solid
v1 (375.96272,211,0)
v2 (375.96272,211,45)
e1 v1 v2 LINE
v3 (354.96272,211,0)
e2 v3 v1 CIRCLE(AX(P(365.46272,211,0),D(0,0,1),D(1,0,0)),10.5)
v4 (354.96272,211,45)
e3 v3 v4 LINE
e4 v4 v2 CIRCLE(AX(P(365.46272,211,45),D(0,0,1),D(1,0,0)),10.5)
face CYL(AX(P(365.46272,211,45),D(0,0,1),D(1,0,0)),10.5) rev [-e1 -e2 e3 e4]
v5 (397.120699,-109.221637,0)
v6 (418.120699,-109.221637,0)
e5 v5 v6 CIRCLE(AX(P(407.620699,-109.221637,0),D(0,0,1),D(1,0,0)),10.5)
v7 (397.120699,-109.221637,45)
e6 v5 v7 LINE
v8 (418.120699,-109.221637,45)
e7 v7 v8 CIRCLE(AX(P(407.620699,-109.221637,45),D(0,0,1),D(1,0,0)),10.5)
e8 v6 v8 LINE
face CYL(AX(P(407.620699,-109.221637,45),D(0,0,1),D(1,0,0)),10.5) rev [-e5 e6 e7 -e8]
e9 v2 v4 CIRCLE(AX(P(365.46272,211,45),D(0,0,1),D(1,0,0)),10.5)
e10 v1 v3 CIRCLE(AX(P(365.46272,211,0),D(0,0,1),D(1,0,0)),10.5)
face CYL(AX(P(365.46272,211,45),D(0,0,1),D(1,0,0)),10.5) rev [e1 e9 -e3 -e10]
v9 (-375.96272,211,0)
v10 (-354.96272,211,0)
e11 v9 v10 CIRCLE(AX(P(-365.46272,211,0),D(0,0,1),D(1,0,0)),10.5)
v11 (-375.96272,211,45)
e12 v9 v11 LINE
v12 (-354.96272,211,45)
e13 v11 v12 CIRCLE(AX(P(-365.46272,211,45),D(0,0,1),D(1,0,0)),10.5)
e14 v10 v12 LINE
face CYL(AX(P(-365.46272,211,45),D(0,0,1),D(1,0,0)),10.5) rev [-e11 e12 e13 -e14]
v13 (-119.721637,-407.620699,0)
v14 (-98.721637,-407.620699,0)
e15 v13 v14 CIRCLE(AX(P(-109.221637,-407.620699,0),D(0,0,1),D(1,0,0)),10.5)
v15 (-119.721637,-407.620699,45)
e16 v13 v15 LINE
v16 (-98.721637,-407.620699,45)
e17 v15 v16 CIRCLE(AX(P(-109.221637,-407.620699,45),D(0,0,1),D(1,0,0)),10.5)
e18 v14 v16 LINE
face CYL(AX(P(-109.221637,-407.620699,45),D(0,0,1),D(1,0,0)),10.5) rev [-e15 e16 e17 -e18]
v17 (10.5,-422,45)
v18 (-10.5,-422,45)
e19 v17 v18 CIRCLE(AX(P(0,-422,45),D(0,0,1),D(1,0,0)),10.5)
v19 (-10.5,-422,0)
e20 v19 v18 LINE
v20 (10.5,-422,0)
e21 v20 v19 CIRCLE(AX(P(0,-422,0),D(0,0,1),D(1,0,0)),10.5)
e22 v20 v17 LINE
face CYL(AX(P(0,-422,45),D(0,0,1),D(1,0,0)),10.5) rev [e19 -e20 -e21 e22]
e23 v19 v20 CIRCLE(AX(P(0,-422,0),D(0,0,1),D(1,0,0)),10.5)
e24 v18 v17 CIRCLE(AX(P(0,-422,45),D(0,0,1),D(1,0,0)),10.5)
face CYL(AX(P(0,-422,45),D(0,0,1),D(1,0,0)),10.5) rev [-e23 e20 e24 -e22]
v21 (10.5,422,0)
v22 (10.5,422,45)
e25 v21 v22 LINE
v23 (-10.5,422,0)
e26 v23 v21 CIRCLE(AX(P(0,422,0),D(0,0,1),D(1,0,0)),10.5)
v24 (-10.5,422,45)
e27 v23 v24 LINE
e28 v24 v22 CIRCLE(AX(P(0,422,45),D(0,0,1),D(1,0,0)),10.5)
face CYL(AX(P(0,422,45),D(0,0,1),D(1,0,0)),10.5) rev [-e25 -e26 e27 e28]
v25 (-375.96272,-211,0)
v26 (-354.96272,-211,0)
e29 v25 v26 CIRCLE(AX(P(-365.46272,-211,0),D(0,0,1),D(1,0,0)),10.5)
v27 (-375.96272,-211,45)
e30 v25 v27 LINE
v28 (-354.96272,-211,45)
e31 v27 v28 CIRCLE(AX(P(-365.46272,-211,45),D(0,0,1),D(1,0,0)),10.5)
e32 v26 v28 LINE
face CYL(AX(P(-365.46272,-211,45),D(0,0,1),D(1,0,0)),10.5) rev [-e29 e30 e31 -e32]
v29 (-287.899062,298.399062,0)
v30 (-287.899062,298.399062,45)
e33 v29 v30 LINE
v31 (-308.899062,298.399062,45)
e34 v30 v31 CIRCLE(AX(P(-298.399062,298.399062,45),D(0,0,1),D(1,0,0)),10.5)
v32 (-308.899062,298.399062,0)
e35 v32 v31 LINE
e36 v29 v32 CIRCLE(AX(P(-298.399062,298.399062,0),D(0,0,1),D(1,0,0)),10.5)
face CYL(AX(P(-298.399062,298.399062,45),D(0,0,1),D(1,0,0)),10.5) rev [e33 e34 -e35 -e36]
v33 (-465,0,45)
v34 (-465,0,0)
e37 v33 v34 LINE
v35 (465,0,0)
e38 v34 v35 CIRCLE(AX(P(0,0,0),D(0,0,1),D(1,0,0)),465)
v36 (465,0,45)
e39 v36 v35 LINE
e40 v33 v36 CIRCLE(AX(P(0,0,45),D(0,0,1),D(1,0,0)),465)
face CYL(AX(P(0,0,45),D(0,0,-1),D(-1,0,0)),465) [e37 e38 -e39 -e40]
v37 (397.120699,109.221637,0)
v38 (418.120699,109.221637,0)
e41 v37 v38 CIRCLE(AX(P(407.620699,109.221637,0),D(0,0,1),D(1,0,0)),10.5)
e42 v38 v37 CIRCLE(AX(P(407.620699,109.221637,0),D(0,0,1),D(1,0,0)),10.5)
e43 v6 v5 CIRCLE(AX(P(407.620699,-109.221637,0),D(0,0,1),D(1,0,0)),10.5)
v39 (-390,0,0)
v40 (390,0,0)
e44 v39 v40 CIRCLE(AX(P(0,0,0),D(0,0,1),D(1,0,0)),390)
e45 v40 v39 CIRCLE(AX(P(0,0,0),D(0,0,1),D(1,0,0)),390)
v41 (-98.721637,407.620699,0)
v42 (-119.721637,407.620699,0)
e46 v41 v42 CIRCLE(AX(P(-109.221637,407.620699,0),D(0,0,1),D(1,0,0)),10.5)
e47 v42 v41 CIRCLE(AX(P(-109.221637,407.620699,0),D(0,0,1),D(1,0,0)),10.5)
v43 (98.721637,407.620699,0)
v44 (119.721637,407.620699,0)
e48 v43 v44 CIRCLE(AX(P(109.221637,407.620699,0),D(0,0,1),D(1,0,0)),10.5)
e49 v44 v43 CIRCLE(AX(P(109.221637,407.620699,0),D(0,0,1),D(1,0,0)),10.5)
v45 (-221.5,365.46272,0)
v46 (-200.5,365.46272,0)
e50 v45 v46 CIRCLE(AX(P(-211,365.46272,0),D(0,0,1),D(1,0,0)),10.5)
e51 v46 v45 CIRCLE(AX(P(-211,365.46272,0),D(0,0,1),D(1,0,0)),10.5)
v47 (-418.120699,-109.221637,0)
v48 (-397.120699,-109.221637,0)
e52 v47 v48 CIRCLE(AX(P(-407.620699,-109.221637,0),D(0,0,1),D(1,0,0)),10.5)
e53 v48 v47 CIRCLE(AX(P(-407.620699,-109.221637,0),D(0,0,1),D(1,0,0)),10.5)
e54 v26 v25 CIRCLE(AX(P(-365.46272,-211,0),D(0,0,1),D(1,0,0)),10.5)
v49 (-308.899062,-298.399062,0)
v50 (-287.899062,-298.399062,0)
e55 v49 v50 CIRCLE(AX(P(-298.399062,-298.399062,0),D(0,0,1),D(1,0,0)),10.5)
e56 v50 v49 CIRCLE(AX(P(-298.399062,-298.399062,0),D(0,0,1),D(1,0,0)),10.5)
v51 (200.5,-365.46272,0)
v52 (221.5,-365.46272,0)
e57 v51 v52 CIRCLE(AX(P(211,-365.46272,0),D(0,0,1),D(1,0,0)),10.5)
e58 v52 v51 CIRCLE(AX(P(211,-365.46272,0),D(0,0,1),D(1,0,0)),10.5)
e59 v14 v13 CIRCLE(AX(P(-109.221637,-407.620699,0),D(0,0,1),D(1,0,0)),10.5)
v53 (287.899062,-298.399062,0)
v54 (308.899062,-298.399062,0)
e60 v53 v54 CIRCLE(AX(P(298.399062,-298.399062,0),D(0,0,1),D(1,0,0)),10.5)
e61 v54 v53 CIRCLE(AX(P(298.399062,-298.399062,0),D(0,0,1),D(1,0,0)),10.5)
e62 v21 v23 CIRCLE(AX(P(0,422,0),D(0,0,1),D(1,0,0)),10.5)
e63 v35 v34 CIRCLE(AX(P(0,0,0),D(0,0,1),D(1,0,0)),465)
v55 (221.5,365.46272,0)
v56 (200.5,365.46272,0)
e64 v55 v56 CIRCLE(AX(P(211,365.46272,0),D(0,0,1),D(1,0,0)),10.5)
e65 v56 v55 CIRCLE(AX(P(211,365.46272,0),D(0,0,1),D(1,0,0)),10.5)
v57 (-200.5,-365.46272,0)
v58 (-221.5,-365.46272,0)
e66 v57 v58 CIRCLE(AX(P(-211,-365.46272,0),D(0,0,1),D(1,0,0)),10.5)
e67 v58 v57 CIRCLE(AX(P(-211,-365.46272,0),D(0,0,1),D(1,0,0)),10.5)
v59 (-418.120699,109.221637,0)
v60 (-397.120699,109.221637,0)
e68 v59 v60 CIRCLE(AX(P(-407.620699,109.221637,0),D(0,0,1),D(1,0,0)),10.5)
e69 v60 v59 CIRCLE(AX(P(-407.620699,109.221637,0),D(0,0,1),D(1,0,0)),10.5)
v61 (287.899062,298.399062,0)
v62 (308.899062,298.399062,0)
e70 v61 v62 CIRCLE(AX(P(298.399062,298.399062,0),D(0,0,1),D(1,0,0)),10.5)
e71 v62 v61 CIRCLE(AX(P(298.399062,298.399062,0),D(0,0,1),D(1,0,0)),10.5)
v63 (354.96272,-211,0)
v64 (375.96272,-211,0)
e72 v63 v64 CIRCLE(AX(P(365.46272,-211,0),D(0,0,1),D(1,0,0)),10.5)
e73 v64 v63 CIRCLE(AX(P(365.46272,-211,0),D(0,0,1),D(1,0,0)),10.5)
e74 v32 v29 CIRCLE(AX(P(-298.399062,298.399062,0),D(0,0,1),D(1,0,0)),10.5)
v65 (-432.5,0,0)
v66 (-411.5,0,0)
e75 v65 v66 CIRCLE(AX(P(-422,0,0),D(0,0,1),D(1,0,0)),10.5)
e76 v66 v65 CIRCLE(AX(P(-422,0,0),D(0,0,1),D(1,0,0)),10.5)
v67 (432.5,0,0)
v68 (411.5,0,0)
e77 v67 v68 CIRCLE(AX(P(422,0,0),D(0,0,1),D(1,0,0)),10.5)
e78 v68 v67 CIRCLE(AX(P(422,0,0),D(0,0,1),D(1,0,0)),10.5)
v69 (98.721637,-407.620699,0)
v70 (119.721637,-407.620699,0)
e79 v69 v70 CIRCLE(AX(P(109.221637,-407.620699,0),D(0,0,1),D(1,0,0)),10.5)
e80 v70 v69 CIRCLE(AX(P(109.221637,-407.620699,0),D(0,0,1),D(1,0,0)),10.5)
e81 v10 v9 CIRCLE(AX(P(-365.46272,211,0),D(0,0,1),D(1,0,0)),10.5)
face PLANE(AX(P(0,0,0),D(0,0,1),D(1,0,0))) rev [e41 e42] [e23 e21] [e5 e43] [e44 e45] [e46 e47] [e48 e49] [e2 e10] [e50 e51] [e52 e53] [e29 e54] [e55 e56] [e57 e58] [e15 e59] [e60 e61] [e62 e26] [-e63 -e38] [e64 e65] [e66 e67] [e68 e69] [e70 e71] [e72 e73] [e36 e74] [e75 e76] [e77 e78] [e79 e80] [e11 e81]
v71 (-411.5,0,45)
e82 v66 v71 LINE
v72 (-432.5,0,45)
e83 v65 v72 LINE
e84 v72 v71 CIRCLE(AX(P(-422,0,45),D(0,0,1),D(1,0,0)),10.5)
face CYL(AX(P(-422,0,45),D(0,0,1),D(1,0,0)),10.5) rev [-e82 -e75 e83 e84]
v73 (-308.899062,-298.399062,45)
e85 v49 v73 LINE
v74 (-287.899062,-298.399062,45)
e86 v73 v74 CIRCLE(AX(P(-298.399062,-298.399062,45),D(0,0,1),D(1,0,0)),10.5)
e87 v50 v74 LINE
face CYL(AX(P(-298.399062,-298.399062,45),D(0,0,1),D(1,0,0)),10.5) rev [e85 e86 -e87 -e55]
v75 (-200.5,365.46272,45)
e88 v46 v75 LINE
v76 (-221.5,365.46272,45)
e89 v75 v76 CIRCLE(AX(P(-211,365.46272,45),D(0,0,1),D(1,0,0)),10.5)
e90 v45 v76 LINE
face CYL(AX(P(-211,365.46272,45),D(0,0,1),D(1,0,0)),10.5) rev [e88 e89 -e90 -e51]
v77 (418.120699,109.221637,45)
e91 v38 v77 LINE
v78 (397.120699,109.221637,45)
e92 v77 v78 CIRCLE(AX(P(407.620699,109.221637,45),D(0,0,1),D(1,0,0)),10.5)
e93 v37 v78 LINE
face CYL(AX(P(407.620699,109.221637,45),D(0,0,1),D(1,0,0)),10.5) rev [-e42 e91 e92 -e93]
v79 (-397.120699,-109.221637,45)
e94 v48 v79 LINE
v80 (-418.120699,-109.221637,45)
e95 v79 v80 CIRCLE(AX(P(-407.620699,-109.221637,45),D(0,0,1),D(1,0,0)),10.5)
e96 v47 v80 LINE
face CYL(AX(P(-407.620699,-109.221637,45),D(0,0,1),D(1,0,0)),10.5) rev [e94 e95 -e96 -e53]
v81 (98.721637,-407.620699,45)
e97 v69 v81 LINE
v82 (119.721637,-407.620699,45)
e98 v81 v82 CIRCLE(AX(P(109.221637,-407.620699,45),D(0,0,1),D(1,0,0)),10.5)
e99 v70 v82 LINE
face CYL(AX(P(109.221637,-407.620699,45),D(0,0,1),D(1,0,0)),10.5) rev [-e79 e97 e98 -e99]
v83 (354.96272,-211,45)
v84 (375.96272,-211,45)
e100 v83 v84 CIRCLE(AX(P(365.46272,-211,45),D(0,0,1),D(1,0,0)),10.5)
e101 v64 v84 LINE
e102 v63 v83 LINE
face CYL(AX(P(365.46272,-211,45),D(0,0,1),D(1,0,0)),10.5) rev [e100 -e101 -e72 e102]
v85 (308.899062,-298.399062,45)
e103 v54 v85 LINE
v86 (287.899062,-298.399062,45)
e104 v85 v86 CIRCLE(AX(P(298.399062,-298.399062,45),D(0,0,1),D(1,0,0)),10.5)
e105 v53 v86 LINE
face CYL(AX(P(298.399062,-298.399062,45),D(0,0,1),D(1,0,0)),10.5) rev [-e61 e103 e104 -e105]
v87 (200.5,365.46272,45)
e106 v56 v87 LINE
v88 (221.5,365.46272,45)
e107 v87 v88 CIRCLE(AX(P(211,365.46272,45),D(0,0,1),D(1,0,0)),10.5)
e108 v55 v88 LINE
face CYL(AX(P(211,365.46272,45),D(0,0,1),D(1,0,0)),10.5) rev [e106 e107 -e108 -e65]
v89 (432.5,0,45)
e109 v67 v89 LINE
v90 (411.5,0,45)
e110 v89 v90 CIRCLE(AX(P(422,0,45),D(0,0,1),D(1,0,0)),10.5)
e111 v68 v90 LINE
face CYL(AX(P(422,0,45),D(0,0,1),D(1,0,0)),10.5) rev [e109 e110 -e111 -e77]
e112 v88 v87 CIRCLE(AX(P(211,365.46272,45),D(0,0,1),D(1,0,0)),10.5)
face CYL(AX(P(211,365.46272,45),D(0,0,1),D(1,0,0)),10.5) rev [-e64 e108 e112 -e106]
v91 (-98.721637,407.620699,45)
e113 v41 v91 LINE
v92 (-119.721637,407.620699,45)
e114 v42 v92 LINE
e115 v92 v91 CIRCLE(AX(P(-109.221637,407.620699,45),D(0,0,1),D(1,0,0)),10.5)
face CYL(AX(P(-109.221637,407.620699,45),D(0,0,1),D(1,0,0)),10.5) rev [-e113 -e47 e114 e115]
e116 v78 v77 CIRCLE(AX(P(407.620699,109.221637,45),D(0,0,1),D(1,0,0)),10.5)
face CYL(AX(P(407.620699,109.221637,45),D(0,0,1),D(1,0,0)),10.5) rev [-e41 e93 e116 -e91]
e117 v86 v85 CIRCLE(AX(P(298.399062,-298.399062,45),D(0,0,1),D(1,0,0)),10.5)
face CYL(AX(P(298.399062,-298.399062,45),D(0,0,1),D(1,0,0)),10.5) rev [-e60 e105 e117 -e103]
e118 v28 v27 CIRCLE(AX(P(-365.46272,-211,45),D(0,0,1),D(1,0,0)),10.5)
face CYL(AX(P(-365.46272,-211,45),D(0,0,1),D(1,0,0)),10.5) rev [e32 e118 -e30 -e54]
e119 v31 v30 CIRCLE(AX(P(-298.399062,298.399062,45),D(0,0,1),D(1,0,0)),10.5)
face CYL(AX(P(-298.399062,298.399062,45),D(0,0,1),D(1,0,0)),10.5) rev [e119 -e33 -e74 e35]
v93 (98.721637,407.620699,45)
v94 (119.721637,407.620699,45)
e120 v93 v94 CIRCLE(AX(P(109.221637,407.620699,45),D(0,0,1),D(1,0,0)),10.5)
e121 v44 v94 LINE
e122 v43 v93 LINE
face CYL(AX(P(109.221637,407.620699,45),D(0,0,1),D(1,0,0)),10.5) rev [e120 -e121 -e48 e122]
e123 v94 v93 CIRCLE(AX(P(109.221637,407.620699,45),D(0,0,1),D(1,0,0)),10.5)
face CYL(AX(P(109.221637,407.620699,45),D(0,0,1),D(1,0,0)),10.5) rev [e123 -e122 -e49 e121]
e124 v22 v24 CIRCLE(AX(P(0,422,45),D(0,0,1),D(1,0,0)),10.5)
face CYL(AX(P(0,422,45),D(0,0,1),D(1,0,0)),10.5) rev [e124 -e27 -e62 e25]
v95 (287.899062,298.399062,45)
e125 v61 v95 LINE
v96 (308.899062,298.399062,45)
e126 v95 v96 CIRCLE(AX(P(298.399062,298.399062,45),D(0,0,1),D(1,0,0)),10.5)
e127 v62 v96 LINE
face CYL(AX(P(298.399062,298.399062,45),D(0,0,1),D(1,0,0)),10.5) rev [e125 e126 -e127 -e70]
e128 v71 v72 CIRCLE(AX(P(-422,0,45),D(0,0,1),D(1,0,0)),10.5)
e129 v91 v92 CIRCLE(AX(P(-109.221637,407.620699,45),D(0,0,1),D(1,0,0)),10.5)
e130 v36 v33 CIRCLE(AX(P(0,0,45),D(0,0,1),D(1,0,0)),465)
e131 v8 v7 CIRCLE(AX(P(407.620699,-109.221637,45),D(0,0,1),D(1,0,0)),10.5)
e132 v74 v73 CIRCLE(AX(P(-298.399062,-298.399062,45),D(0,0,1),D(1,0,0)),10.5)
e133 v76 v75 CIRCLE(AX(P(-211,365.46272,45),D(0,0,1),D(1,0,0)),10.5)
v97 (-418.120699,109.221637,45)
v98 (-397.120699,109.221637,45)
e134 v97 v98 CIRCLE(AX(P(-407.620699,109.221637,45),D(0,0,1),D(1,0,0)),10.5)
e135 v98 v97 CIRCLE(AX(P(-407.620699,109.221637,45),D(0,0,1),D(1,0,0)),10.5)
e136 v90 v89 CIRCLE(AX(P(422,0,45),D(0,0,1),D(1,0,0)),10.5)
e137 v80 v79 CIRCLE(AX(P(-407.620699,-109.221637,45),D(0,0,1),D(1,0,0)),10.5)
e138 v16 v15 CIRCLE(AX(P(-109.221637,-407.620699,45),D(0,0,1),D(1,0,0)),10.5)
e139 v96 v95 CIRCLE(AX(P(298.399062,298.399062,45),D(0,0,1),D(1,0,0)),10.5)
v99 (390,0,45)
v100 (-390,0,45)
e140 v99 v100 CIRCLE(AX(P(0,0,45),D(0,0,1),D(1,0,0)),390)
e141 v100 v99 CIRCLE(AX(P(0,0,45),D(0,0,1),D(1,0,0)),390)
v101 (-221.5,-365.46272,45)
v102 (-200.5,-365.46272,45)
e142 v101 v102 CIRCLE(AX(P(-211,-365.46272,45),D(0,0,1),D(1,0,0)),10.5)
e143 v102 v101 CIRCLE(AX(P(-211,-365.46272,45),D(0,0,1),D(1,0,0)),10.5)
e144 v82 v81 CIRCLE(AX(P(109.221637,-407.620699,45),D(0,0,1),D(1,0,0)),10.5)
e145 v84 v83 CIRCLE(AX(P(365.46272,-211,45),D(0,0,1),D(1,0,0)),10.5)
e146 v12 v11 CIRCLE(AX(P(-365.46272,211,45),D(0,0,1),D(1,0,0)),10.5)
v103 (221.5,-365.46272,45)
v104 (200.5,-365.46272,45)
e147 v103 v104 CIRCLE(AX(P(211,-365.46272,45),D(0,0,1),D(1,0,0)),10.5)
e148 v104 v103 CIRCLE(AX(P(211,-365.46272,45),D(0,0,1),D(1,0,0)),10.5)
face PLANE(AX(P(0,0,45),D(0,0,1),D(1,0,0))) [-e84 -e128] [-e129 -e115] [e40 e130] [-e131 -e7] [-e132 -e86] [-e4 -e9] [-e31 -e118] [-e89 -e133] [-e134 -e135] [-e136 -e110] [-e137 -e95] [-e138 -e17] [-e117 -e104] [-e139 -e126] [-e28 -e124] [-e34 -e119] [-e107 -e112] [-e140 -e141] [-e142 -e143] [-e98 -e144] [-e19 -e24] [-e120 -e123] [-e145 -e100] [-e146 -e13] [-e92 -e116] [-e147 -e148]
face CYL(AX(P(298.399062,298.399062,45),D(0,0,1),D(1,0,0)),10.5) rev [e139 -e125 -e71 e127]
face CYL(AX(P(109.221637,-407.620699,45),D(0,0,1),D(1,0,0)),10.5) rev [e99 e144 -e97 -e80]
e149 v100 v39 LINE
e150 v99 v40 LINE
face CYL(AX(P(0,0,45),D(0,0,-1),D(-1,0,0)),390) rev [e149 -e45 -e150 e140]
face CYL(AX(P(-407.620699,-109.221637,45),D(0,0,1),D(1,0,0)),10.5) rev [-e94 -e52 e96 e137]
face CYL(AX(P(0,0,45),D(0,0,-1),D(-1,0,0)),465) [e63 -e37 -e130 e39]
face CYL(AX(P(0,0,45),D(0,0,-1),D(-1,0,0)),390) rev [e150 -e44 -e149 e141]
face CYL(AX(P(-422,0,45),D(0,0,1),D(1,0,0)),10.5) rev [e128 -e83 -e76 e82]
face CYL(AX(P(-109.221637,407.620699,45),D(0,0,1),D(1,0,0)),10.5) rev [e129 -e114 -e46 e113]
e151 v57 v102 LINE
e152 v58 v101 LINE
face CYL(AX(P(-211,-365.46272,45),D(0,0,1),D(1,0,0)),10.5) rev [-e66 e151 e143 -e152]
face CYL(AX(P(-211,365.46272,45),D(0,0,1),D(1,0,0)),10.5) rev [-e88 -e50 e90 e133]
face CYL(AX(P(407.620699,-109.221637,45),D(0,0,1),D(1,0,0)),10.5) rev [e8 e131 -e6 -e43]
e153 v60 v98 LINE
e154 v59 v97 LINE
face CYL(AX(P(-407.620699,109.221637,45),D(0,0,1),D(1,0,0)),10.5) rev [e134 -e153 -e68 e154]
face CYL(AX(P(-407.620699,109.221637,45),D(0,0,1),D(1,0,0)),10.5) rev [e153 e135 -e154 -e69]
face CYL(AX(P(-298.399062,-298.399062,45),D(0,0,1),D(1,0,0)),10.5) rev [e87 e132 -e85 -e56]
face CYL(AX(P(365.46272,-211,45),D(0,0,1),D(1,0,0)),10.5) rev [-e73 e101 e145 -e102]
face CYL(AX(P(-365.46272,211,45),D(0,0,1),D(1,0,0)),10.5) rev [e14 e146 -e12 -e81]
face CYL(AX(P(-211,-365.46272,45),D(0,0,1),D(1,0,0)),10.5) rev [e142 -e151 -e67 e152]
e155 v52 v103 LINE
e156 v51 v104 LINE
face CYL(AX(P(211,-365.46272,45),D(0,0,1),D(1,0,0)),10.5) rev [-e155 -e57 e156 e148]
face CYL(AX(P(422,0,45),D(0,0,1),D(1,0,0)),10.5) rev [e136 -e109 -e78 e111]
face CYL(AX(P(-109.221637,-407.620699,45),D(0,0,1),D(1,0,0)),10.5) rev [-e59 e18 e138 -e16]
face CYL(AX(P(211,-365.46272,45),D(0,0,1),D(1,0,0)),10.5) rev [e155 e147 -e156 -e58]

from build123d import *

# Parameters (mm, degrees)
SKETCH1_R               = 465
SKETCH1_R_2             = 390
BOSS_EXTRUDE1_DEPTH     = 45
M24_THREADED_HOLE1_D    = 21
CIRCULAR_PATTERN1_COUNT = 24


with BuildPart() as part:
    # Sketch1 → Boss-Extrude1 (new body)
    with BuildSketch(Plane.XY):
        with Locations(Location((0, 0, 0), (0, 0, 180))):
            Circle(SKETCH1_R)
        with Locations(Location((0, 0, 0), (0, 0, 180))):
            Circle(SKETCH1_R_2, mode=Mode.SUBTRACT)
    extrude(amount=BOSS_EXTRUDE1_DEPTH)

    # M24 Threaded hole1 (through all)
    with Locations(Plane(origin=(-422, 0, 45), x_dir=(1, 0, 0), z_dir=(0, 0, 1))):
        with Locations((0, 0)):
            m24_threaded_hole1 = Hole(M24_THREADED_HOLE1_D / 2)

    # Circular pattern1: M24 Threaded hole1 ×24 about axis
    circular_pattern1_axis = Axis((0, 0, 0), (0, 0, 1))
    for i in range(1, CIRCULAR_PATTERN1_COUNT):
        add(m24_threaded_hole1.rotate(circular_pattern1_axis, i * 360 / CIRCULAR_PATTERN1_COUNT), mode=Mode.SUBTRACT)


solid = part.part
